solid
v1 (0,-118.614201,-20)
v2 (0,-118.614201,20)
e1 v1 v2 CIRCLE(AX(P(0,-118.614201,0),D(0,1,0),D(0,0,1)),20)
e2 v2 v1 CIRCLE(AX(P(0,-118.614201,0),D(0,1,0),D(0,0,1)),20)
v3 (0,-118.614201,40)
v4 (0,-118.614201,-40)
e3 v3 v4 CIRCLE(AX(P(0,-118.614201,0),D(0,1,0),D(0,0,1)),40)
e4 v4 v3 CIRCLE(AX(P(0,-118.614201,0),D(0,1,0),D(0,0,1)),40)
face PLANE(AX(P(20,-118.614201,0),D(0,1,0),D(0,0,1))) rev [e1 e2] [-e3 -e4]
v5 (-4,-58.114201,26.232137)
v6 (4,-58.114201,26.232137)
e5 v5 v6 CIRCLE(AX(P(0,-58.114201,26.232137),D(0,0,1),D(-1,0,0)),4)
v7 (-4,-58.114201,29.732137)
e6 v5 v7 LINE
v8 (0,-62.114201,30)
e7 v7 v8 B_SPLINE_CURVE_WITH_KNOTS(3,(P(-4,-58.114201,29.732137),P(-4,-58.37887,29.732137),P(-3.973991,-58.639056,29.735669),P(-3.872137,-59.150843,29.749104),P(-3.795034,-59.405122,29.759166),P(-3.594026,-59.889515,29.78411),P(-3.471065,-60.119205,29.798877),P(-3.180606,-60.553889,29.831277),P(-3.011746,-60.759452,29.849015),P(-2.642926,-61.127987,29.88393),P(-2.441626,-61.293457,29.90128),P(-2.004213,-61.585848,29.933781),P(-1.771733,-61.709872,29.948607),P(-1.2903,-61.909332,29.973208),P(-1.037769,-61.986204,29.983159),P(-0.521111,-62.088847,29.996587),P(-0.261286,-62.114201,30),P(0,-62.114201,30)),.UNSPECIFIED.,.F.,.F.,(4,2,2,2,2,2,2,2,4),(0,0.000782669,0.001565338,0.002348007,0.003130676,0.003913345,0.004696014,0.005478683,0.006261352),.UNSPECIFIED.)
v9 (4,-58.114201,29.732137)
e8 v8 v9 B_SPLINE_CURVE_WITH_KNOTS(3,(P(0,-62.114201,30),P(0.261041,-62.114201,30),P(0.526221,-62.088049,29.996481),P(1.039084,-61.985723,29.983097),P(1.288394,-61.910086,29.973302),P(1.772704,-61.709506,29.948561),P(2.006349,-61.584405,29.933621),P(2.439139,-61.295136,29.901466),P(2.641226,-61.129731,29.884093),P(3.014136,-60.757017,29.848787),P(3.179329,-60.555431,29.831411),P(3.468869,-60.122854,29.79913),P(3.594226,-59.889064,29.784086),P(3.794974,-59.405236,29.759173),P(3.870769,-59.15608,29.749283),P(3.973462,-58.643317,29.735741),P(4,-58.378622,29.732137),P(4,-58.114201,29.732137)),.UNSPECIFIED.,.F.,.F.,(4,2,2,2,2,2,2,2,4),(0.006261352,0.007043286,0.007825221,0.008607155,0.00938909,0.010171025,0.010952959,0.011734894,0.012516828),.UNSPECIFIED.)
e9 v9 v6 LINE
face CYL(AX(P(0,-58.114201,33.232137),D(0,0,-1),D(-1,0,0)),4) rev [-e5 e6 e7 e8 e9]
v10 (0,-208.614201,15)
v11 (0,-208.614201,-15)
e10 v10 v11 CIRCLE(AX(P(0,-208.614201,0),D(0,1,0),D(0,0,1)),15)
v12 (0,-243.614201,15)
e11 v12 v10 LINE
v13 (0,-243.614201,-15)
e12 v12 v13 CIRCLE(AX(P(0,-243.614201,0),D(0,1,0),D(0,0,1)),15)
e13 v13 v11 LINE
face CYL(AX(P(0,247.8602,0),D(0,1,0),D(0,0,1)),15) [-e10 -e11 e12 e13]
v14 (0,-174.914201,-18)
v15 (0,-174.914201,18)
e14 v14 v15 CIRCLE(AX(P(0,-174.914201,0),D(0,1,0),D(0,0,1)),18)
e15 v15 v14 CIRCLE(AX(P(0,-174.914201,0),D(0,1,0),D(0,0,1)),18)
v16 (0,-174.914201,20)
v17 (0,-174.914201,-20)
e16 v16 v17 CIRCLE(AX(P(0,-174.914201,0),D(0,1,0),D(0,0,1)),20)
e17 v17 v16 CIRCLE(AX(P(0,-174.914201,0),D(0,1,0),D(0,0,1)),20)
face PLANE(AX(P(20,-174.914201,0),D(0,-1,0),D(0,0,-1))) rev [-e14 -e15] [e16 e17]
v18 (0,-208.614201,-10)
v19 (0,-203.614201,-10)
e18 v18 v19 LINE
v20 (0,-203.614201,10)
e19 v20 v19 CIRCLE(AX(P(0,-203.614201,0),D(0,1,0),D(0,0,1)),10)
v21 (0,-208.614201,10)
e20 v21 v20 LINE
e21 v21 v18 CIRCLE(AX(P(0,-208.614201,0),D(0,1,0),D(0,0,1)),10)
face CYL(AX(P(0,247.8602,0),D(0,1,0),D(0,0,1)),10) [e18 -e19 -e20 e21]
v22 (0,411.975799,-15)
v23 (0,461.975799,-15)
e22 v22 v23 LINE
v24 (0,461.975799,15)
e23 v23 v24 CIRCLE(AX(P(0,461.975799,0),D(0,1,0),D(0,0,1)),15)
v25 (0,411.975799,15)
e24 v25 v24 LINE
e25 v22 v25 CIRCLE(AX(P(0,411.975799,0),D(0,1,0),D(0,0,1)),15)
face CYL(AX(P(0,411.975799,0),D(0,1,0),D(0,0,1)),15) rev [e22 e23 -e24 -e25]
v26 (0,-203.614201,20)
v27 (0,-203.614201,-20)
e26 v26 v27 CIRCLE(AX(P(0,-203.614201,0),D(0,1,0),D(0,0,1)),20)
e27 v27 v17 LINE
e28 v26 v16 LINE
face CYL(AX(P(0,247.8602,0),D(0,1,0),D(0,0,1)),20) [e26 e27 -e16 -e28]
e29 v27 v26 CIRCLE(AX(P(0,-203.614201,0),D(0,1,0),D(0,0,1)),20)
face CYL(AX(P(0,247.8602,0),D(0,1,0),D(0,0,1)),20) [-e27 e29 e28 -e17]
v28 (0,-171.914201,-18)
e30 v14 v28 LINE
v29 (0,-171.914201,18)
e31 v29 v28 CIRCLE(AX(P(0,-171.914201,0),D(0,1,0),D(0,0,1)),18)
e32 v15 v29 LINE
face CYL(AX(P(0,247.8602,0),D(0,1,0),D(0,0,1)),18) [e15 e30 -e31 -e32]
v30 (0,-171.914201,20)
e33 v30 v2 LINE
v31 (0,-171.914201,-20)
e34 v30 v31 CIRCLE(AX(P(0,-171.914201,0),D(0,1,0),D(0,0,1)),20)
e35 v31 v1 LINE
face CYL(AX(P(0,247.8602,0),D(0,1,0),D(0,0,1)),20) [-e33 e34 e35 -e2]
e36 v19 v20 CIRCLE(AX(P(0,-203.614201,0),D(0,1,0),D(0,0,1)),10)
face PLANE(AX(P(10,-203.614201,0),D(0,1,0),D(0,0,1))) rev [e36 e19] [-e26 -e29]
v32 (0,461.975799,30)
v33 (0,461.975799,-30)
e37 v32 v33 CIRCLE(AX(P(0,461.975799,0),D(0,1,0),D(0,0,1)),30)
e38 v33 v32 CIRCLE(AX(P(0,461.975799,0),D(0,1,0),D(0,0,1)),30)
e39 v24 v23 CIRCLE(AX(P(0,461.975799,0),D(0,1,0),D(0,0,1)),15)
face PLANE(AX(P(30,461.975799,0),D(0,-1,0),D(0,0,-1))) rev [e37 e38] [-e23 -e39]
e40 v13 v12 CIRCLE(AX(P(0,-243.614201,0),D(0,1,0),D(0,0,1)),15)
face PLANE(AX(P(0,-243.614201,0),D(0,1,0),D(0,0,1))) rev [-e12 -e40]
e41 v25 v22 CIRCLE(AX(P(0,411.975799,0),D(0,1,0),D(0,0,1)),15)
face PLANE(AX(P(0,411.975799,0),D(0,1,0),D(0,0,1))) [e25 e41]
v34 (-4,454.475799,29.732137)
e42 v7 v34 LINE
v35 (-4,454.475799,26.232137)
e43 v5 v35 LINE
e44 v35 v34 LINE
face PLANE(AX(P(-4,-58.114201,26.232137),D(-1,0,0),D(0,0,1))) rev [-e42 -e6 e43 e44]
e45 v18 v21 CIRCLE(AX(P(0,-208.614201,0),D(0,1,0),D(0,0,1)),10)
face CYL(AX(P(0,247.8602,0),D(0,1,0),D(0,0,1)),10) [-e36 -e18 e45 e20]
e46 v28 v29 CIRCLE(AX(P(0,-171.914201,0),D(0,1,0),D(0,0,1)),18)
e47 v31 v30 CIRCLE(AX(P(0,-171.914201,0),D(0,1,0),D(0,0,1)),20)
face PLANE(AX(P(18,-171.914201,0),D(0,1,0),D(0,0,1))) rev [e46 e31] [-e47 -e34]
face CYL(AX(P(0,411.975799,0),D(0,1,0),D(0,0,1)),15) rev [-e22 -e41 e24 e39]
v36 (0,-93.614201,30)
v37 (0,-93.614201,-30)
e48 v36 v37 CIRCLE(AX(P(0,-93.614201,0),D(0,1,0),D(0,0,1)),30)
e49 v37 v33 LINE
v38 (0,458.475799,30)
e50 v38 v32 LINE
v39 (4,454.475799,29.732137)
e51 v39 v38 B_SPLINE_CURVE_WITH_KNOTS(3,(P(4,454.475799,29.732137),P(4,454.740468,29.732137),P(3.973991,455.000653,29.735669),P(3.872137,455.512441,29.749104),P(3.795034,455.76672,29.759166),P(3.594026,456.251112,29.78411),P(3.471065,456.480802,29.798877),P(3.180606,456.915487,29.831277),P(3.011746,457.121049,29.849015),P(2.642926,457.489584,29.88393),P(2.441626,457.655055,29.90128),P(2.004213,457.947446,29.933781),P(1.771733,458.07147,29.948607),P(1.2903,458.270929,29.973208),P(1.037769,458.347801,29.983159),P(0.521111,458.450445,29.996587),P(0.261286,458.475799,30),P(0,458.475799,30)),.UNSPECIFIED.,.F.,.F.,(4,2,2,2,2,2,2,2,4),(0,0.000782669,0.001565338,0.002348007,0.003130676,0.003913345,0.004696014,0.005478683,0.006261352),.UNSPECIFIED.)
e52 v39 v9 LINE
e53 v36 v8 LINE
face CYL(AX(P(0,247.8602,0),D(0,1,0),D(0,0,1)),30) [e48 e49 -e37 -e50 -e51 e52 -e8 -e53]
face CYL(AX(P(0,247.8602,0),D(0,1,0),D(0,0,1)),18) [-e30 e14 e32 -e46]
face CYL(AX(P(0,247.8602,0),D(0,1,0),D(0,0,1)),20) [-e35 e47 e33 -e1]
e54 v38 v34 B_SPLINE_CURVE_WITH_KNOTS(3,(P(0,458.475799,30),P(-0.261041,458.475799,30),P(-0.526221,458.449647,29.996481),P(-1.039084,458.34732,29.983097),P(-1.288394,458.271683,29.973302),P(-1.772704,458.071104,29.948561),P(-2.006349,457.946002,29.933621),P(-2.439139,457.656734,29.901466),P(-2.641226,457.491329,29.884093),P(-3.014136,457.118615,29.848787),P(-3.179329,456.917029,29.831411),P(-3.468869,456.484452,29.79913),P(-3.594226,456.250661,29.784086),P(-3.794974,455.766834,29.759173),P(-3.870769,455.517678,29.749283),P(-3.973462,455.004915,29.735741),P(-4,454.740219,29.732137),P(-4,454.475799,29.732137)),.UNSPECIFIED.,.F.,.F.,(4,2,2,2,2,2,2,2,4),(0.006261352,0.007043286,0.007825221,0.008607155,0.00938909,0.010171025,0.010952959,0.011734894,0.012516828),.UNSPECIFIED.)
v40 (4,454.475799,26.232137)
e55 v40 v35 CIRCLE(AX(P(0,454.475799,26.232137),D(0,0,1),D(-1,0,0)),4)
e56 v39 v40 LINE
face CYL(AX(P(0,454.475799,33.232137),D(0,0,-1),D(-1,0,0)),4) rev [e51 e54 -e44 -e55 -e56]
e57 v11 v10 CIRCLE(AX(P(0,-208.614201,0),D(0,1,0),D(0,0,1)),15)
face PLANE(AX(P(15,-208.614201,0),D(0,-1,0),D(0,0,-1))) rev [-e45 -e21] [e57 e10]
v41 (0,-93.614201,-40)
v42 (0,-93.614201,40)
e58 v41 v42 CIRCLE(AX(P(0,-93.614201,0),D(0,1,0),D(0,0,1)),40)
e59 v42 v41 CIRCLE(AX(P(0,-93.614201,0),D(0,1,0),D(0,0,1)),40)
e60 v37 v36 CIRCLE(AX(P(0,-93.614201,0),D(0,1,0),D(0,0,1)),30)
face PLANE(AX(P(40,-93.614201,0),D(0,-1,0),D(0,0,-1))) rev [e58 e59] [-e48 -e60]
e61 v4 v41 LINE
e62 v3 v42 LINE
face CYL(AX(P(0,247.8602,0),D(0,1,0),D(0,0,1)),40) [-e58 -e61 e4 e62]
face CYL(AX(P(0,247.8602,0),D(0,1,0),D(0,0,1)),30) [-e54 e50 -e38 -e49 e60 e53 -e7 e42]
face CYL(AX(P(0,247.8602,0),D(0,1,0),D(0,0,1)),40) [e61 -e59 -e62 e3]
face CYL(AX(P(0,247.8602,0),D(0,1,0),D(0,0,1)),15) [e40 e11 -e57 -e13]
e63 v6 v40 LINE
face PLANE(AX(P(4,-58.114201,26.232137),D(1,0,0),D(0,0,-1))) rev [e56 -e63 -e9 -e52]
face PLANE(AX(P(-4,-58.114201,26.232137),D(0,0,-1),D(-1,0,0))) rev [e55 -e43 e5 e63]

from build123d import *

# Parameters (mm, degrees)
SKETCH_2_R          = 15
CUT_EXTRUDE_1_DEPTH = 50
CUT_EXTRUDE_START   = -7.5
SKETCH_3_W          = 8
SKETCH_3_H          = 7
CUT_EXTRUDE_2_DEPTH = 512.59
CUT_EXTRUDE_3_DEPTH = 7


with BuildPart() as part:
    # 草图1 → 旋转1 (revolve)
    with BuildSketch(Plane.XY, mode=Mode.PRIVATE) as revolve_1_sk:
        Polygon((0, -243.614201173), (15, -243.614201173), (15, -208.614201173), (10, -208.614201173), (10, -203.614201173), (20, -203.614201173), (20, -174.914201173), (18, -174.914201173), (18, -171.914201173), (20, -171.914201173), (20, -118.614201173), (40, -118.614201173), (40, -93.614201173), (30, -93.614201173), (30, 461.975798827), (0, 461.975798827), align=None)
    revolve(revolve_1_sk.sketch.rotate(Axis((0, 247.860200322, 0), (0, -1, 0)), 90), axis=Axis((0, 247.860200322, 0), (0, -1, 0)))

    # 草图2 → 切除-拉伸1 (cut)
    with BuildSketch(Plane(origin=(0, 461.975798827, 0), x_dir=(1, 0, 0), z_dir=(0, 1, 0))):
        with Locations(Location((0, 0, 0), (0, 0, 270))):
            Circle(SKETCH_2_R)
    extrude(amount=-CUT_EXTRUDE_1_DEPTH, mode=Mode.SUBTRACT)

    # 草图3 → 切除-拉伸2 (cut)
    with BuildSketch(Plane(origin=(0, 461.975798827, 0), x_dir=(1, 0, 0), z_dir=(0, 1, 0)).offset(CUT_EXTRUDE_START)):
        with Locations((0, -29.732137495)):
            Rectangle(SKETCH_3_W, SKETCH_3_H)
    extrude(amount=-CUT_EXTRUDE_2_DEPTH, mode=Mode.SUBTRACT)

    # 草图4 → 切除-拉伸3 (cut)
    with BuildSketch(Plane.XY.offset(26.232137495)):
        with BuildLine():
            Line((4, -58.114201173), (-4, -58.114201173))
            ThreePointArc((-4, -58.114201173), (0, -62.114201173), (4, -58.114201173))
        make_face()
        with BuildLine():
            Line((-4, 454.475798827), (4, 454.475798827))
            ThreePointArc((4, 454.475798827), (0, 458.475798827), (-4, 454.475798827))
        make_face()
    extrude(amount=CUT_EXTRUDE_3_DEPTH, mode=Mode.SUBTRACT)


solid = part.part
